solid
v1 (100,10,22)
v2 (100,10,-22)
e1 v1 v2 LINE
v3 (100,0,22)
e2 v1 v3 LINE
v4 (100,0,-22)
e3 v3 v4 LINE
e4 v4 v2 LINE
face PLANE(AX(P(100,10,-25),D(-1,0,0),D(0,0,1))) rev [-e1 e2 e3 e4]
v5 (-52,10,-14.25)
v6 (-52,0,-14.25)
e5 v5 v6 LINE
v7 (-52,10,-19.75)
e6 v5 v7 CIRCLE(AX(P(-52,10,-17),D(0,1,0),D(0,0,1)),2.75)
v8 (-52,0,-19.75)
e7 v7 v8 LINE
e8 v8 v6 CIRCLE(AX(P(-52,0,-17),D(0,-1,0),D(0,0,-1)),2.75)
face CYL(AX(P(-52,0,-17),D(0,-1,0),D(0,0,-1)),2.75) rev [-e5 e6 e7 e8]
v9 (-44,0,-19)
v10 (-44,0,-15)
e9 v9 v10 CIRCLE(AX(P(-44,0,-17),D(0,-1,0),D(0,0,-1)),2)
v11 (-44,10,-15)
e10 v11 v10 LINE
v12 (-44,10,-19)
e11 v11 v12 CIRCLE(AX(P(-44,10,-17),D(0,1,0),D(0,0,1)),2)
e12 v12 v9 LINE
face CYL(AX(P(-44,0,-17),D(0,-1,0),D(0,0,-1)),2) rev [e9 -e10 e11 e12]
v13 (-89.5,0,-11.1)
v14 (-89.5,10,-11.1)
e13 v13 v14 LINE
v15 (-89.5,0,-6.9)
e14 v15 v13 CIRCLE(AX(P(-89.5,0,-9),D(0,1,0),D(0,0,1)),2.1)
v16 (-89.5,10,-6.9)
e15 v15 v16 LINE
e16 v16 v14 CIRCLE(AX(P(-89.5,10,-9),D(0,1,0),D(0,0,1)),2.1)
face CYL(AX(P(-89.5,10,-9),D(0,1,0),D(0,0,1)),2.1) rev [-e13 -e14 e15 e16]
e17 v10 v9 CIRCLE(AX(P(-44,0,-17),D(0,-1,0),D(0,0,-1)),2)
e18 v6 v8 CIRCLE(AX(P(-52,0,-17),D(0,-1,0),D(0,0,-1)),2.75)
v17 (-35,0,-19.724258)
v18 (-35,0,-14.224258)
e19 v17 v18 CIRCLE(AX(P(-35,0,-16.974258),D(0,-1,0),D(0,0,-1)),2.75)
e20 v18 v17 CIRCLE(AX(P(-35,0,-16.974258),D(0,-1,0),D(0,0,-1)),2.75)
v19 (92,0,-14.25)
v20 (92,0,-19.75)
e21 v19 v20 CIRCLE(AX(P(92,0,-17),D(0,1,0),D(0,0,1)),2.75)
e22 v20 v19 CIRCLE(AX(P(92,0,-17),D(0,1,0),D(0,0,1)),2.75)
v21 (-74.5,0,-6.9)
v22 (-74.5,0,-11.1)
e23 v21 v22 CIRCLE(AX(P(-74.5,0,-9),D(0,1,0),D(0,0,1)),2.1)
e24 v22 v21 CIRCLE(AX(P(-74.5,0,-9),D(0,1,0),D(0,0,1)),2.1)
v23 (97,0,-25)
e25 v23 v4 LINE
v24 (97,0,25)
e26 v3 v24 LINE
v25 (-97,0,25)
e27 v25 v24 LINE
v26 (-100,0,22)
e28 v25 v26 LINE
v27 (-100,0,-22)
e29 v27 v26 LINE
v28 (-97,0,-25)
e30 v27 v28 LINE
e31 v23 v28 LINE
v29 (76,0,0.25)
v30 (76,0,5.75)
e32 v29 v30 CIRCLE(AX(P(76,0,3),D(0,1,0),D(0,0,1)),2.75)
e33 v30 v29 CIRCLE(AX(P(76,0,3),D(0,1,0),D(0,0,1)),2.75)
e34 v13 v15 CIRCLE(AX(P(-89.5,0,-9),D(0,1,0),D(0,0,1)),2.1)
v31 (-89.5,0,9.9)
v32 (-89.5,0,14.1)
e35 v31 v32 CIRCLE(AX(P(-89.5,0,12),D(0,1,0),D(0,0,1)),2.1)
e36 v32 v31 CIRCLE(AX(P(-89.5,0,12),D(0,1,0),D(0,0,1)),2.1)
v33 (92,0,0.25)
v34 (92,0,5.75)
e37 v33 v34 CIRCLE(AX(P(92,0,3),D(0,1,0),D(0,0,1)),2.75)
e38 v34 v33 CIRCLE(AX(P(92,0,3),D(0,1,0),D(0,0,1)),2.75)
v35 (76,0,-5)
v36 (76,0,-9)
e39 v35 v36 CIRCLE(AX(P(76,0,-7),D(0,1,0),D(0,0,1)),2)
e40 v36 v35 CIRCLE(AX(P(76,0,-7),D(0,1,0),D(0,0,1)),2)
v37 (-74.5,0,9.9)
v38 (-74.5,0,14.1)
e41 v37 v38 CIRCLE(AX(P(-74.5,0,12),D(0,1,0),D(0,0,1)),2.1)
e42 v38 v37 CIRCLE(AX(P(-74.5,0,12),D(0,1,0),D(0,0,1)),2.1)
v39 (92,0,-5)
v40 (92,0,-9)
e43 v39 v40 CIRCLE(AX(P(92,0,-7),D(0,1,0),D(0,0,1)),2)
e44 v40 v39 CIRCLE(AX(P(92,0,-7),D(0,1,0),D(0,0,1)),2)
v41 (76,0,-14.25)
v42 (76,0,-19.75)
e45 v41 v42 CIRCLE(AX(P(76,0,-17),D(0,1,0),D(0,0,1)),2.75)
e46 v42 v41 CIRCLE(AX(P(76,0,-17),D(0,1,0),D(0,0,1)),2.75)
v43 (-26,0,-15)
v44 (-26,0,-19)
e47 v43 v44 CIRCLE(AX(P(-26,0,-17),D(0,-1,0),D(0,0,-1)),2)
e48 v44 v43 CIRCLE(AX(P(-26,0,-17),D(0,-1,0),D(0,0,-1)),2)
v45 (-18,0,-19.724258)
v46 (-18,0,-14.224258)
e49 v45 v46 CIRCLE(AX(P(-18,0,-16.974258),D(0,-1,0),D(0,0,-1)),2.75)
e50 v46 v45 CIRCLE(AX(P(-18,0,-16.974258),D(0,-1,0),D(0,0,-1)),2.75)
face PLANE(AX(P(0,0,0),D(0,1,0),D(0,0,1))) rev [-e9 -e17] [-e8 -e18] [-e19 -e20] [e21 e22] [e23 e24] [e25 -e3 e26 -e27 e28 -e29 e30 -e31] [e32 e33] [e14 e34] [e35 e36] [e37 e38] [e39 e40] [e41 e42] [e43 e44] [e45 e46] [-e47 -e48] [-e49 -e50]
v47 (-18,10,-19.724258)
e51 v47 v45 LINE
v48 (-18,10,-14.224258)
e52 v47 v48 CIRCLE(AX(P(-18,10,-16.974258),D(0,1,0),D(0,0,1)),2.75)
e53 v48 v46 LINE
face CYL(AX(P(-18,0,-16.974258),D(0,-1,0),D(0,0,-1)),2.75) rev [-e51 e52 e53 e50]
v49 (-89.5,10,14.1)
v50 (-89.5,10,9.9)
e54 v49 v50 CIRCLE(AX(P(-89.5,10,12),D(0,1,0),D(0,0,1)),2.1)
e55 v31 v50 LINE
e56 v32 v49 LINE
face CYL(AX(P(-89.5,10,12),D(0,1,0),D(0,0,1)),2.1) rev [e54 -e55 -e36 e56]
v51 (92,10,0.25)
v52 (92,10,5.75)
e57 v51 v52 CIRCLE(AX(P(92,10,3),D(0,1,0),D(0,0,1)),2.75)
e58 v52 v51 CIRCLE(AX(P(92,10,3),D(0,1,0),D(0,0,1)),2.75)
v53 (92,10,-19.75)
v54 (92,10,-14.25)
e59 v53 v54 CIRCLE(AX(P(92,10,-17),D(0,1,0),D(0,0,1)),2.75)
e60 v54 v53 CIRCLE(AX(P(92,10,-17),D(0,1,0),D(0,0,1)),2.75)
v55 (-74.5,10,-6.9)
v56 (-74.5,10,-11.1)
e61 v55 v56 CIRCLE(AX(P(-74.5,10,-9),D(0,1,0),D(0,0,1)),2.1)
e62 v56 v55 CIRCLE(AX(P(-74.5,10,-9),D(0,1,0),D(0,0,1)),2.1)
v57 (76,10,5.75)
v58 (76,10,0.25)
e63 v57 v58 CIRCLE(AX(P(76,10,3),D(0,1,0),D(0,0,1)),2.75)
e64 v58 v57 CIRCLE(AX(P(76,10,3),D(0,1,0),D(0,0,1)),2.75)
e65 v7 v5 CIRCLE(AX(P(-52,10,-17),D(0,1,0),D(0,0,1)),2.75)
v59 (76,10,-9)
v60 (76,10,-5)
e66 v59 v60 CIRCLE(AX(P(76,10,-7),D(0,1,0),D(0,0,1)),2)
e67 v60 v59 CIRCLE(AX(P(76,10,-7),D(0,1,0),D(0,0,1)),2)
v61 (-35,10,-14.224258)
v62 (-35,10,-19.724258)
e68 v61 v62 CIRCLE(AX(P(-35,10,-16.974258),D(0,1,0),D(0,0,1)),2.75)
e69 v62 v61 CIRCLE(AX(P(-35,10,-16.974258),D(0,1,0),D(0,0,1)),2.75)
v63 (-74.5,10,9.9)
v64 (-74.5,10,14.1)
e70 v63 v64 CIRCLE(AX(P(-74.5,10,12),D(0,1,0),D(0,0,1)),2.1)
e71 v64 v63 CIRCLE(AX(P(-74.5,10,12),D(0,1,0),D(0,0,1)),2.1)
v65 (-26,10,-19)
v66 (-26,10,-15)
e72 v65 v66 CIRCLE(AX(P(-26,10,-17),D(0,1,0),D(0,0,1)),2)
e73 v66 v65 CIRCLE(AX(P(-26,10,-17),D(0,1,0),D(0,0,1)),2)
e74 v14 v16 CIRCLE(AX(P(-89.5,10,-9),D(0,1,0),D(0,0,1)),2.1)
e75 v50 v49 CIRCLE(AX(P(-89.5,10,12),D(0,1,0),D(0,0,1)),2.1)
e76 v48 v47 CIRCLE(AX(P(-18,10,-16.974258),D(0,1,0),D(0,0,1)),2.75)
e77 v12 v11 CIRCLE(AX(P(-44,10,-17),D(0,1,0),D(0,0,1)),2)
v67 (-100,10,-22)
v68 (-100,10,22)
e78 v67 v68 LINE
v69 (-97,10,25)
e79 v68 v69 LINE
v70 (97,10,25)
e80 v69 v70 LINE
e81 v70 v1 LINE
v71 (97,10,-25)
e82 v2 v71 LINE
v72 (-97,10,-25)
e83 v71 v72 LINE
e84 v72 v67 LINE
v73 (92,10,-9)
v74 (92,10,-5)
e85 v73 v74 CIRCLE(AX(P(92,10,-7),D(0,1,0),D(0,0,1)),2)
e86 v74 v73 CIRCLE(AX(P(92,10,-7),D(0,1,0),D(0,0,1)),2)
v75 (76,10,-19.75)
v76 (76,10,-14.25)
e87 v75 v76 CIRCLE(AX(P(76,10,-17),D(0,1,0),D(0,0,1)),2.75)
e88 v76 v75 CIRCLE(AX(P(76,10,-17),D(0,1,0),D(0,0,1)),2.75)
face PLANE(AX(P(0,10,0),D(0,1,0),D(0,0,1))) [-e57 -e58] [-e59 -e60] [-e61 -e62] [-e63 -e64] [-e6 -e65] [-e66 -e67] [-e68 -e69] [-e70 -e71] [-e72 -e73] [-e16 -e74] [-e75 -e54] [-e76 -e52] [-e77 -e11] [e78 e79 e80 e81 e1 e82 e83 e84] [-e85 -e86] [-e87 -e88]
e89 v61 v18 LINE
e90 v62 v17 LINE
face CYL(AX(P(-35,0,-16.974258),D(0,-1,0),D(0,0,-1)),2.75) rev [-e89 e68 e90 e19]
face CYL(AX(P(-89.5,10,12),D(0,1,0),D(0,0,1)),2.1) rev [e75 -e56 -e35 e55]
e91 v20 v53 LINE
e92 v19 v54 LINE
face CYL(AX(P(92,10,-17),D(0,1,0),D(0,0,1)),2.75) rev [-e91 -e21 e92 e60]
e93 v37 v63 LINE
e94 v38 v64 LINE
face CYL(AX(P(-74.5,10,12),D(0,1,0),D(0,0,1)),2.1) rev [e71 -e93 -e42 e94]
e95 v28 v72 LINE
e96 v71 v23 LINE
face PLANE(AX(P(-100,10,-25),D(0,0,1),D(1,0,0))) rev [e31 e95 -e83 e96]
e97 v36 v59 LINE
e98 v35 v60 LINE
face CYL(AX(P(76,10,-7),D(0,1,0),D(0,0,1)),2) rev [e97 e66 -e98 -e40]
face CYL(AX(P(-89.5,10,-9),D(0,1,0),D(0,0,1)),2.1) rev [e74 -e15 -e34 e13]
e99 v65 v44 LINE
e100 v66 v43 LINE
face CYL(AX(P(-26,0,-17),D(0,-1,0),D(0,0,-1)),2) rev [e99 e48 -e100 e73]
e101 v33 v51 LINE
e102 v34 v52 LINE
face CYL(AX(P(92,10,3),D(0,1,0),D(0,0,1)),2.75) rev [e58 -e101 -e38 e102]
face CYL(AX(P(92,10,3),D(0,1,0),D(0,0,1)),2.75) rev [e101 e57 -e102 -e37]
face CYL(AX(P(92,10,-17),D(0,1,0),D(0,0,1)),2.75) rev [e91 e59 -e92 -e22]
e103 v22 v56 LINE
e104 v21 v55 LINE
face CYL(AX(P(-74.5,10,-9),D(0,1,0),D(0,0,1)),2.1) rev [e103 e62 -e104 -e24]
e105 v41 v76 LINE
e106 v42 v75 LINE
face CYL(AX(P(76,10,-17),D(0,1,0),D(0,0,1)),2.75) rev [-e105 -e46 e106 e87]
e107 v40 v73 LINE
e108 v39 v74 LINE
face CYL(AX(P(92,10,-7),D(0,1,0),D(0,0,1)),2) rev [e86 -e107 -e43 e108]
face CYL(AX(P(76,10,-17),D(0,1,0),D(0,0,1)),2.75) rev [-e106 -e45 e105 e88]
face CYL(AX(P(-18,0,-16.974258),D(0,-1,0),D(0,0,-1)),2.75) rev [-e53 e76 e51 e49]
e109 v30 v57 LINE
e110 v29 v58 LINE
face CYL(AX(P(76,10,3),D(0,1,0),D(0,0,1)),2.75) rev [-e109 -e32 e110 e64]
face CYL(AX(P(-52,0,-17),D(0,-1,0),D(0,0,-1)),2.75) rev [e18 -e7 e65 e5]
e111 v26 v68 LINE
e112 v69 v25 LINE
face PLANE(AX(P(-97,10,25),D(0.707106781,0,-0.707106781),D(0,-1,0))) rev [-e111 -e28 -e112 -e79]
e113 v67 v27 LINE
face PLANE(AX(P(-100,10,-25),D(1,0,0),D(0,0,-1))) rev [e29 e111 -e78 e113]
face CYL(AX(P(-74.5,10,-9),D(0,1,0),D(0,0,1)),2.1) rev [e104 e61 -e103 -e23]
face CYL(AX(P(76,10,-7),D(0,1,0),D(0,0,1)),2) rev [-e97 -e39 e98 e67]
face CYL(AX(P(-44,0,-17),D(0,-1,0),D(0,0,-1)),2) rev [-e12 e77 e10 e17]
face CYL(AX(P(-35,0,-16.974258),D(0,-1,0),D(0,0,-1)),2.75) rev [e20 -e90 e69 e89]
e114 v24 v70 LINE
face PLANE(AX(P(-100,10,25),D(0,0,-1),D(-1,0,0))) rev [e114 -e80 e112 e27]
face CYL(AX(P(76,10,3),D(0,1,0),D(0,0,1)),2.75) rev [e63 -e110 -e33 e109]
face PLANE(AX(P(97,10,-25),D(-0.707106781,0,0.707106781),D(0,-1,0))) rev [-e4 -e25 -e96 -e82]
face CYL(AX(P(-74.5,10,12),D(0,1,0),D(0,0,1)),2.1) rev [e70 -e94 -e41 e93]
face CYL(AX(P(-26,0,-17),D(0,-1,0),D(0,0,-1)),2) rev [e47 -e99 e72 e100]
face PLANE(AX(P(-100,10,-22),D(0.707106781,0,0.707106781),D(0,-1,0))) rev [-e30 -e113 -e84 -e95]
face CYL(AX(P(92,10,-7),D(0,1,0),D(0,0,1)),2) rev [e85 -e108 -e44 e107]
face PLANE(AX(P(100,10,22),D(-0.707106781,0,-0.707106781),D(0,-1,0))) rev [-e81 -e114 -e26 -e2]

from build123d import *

# Parameters (mm, degrees)
SKETCH_6_W                  = 200
SKETCH_6_H                  = 50
EXTRUDE_1_DEPTH             = 10
CHAMFER_1_SIZE              = 3
HOLE_WIZARD_5_5_5_5_1_D     = 5.5
HOLE_WIZARD_5_5_5_5_1_DEPTH = 12.4
HOLE_WIZARD_5_5_5_5_1_TIP   = 1.652366702
MM_2_D                      = 4
MM_2_DEPTH                  = 12.4
MM_2_TIP                    = 1.201721238
HOLE_WIZARD_M5_2_D          = 4.2
HOLE_WIZARD_M5_2_DEPTH      = 12.4
HOLE_WIZARD_M5_2_TIP        = 1.2618073
HOLE_WIZARD_5_5_5_5_2_D     = 5.5
HOLE_WIZARD_5_5_5_5_2_DEPTH = 12.4
HOLE_WIZARD_5_5_5_5_2_TIP   = 1.652366702
MM_3_D                      = 4
MM_3_DEPTH                  = 12.4
MM_3_TIP                    = 1.201721238


with BuildPart() as part:
    # 草图6 → 凸台-拉伸1 (new body)
    with BuildSketch(Plane(origin=(0, 0, 0), x_dir=(1, 0, 0), z_dir=(0, 1, 0))):
        Rectangle(SKETCH_6_W, SKETCH_6_H)
    extrude(amount=EXTRUDE_1_DEPTH)

    # 倒角1
    chamfer_1_edges = [part.edges().sort_by_distance(p)[0] for p in [
        (100, 5, 25),
        (-100, 5, 25),
        (-100, 5, -25),
        (100, 5, -25),
    ]]
    chamfer(chamfer_1_edges, length=CHAMFER_1_SIZE)

    # Ø5.5 (5.5) 直径孔1
    with Locations(Plane(origin=(0, 10, 0), x_dir=(1, 0, 0), z_dir=(0, 1, 0))):
        with Locations((76, 17), (76, -3), (92, -3), (92, 17)):
            Hole(HOLE_WIZARD_5_5_5_5_1_D / 2, depth=HOLE_WIZARD_5_5_5_5_1_DEPTH)
            with Locations((0, 0, -(HOLE_WIZARD_5_5_5_5_1_DEPTH + HOLE_WIZARD_5_5_5_5_1_TIP / 2))):  # 118° drill point
                Cone(0, HOLE_WIZARD_5_5_5_5_1_D / 2, HOLE_WIZARD_5_5_5_5_1_TIP, mode=Mode.SUBTRACT)

    # 大小mm 暗销孔2
    with Locations(Plane(origin=(0, 10, 0), x_dir=(1, 0, 0), z_dir=(0, 1, 0))):
        with Locations((76, 7), (92, 7)):
            Hole(MM_2_D / 2, depth=MM_2_DEPTH)
            with Locations((0, 0, -(MM_2_DEPTH + MM_2_TIP / 2))):  # 118° drill point
                Cone(0, MM_2_D / 2, MM_2_TIP, mode=Mode.SUBTRACT)

    # M5 螺纹孔2
    with Locations(Plane(origin=(0, 10, 0), x_dir=(1, 0, 0), z_dir=(0, 1, 0))):
        with Locations((-89.5, 9), (-74.5, 9), (-89.5, -12), (-74.5, -12)):
            Hole(HOLE_WIZARD_M5_2_D / 2, depth=HOLE_WIZARD_M5_2_DEPTH)
            with Locations((0, 0, -(HOLE_WIZARD_M5_2_DEPTH + HOLE_WIZARD_M5_2_TIP / 2))):  # 118° drill point
                Cone(0, HOLE_WIZARD_M5_2_D / 2, HOLE_WIZARD_M5_2_TIP, mode=Mode.SUBTRACT)

    # Ø5.5 (5.5) 直径孔2
    with Locations(Plane(origin=(0, 0, 0), x_dir=(-1, 0, 0), z_dir=(0, -1, 0))):
        with Locations((52, 17), (35, 16.974257895), (18, 16.974257895)):
            Hole(HOLE_WIZARD_5_5_5_5_2_D / 2, depth=HOLE_WIZARD_5_5_5_5_2_DEPTH)
            with Locations((0, 0, -(HOLE_WIZARD_5_5_5_5_2_DEPTH + HOLE_WIZARD_5_5_5_5_2_TIP / 2))):  # 118° drill point
                Cone(0, HOLE_WIZARD_5_5_5_5_2_D / 2, HOLE_WIZARD_5_5_5_5_2_TIP, mode=Mode.SUBTRACT)

    # 大小mm 暗销孔3
    with Locations(Plane(origin=(0, 0, 0), x_dir=(-1, 0, 0), z_dir=(0, -1, 0))):
        with Locations((44, 17), (26, 17)):
            Hole(MM_3_D / 2, depth=MM_3_DEPTH)
            with Locations((0, 0, -(MM_3_DEPTH + MM_3_TIP / 2))):  # 118° drill point
                Cone(0, MM_3_D / 2, MM_3_TIP, mode=Mode.SUBTRACT)


solid = part.part
